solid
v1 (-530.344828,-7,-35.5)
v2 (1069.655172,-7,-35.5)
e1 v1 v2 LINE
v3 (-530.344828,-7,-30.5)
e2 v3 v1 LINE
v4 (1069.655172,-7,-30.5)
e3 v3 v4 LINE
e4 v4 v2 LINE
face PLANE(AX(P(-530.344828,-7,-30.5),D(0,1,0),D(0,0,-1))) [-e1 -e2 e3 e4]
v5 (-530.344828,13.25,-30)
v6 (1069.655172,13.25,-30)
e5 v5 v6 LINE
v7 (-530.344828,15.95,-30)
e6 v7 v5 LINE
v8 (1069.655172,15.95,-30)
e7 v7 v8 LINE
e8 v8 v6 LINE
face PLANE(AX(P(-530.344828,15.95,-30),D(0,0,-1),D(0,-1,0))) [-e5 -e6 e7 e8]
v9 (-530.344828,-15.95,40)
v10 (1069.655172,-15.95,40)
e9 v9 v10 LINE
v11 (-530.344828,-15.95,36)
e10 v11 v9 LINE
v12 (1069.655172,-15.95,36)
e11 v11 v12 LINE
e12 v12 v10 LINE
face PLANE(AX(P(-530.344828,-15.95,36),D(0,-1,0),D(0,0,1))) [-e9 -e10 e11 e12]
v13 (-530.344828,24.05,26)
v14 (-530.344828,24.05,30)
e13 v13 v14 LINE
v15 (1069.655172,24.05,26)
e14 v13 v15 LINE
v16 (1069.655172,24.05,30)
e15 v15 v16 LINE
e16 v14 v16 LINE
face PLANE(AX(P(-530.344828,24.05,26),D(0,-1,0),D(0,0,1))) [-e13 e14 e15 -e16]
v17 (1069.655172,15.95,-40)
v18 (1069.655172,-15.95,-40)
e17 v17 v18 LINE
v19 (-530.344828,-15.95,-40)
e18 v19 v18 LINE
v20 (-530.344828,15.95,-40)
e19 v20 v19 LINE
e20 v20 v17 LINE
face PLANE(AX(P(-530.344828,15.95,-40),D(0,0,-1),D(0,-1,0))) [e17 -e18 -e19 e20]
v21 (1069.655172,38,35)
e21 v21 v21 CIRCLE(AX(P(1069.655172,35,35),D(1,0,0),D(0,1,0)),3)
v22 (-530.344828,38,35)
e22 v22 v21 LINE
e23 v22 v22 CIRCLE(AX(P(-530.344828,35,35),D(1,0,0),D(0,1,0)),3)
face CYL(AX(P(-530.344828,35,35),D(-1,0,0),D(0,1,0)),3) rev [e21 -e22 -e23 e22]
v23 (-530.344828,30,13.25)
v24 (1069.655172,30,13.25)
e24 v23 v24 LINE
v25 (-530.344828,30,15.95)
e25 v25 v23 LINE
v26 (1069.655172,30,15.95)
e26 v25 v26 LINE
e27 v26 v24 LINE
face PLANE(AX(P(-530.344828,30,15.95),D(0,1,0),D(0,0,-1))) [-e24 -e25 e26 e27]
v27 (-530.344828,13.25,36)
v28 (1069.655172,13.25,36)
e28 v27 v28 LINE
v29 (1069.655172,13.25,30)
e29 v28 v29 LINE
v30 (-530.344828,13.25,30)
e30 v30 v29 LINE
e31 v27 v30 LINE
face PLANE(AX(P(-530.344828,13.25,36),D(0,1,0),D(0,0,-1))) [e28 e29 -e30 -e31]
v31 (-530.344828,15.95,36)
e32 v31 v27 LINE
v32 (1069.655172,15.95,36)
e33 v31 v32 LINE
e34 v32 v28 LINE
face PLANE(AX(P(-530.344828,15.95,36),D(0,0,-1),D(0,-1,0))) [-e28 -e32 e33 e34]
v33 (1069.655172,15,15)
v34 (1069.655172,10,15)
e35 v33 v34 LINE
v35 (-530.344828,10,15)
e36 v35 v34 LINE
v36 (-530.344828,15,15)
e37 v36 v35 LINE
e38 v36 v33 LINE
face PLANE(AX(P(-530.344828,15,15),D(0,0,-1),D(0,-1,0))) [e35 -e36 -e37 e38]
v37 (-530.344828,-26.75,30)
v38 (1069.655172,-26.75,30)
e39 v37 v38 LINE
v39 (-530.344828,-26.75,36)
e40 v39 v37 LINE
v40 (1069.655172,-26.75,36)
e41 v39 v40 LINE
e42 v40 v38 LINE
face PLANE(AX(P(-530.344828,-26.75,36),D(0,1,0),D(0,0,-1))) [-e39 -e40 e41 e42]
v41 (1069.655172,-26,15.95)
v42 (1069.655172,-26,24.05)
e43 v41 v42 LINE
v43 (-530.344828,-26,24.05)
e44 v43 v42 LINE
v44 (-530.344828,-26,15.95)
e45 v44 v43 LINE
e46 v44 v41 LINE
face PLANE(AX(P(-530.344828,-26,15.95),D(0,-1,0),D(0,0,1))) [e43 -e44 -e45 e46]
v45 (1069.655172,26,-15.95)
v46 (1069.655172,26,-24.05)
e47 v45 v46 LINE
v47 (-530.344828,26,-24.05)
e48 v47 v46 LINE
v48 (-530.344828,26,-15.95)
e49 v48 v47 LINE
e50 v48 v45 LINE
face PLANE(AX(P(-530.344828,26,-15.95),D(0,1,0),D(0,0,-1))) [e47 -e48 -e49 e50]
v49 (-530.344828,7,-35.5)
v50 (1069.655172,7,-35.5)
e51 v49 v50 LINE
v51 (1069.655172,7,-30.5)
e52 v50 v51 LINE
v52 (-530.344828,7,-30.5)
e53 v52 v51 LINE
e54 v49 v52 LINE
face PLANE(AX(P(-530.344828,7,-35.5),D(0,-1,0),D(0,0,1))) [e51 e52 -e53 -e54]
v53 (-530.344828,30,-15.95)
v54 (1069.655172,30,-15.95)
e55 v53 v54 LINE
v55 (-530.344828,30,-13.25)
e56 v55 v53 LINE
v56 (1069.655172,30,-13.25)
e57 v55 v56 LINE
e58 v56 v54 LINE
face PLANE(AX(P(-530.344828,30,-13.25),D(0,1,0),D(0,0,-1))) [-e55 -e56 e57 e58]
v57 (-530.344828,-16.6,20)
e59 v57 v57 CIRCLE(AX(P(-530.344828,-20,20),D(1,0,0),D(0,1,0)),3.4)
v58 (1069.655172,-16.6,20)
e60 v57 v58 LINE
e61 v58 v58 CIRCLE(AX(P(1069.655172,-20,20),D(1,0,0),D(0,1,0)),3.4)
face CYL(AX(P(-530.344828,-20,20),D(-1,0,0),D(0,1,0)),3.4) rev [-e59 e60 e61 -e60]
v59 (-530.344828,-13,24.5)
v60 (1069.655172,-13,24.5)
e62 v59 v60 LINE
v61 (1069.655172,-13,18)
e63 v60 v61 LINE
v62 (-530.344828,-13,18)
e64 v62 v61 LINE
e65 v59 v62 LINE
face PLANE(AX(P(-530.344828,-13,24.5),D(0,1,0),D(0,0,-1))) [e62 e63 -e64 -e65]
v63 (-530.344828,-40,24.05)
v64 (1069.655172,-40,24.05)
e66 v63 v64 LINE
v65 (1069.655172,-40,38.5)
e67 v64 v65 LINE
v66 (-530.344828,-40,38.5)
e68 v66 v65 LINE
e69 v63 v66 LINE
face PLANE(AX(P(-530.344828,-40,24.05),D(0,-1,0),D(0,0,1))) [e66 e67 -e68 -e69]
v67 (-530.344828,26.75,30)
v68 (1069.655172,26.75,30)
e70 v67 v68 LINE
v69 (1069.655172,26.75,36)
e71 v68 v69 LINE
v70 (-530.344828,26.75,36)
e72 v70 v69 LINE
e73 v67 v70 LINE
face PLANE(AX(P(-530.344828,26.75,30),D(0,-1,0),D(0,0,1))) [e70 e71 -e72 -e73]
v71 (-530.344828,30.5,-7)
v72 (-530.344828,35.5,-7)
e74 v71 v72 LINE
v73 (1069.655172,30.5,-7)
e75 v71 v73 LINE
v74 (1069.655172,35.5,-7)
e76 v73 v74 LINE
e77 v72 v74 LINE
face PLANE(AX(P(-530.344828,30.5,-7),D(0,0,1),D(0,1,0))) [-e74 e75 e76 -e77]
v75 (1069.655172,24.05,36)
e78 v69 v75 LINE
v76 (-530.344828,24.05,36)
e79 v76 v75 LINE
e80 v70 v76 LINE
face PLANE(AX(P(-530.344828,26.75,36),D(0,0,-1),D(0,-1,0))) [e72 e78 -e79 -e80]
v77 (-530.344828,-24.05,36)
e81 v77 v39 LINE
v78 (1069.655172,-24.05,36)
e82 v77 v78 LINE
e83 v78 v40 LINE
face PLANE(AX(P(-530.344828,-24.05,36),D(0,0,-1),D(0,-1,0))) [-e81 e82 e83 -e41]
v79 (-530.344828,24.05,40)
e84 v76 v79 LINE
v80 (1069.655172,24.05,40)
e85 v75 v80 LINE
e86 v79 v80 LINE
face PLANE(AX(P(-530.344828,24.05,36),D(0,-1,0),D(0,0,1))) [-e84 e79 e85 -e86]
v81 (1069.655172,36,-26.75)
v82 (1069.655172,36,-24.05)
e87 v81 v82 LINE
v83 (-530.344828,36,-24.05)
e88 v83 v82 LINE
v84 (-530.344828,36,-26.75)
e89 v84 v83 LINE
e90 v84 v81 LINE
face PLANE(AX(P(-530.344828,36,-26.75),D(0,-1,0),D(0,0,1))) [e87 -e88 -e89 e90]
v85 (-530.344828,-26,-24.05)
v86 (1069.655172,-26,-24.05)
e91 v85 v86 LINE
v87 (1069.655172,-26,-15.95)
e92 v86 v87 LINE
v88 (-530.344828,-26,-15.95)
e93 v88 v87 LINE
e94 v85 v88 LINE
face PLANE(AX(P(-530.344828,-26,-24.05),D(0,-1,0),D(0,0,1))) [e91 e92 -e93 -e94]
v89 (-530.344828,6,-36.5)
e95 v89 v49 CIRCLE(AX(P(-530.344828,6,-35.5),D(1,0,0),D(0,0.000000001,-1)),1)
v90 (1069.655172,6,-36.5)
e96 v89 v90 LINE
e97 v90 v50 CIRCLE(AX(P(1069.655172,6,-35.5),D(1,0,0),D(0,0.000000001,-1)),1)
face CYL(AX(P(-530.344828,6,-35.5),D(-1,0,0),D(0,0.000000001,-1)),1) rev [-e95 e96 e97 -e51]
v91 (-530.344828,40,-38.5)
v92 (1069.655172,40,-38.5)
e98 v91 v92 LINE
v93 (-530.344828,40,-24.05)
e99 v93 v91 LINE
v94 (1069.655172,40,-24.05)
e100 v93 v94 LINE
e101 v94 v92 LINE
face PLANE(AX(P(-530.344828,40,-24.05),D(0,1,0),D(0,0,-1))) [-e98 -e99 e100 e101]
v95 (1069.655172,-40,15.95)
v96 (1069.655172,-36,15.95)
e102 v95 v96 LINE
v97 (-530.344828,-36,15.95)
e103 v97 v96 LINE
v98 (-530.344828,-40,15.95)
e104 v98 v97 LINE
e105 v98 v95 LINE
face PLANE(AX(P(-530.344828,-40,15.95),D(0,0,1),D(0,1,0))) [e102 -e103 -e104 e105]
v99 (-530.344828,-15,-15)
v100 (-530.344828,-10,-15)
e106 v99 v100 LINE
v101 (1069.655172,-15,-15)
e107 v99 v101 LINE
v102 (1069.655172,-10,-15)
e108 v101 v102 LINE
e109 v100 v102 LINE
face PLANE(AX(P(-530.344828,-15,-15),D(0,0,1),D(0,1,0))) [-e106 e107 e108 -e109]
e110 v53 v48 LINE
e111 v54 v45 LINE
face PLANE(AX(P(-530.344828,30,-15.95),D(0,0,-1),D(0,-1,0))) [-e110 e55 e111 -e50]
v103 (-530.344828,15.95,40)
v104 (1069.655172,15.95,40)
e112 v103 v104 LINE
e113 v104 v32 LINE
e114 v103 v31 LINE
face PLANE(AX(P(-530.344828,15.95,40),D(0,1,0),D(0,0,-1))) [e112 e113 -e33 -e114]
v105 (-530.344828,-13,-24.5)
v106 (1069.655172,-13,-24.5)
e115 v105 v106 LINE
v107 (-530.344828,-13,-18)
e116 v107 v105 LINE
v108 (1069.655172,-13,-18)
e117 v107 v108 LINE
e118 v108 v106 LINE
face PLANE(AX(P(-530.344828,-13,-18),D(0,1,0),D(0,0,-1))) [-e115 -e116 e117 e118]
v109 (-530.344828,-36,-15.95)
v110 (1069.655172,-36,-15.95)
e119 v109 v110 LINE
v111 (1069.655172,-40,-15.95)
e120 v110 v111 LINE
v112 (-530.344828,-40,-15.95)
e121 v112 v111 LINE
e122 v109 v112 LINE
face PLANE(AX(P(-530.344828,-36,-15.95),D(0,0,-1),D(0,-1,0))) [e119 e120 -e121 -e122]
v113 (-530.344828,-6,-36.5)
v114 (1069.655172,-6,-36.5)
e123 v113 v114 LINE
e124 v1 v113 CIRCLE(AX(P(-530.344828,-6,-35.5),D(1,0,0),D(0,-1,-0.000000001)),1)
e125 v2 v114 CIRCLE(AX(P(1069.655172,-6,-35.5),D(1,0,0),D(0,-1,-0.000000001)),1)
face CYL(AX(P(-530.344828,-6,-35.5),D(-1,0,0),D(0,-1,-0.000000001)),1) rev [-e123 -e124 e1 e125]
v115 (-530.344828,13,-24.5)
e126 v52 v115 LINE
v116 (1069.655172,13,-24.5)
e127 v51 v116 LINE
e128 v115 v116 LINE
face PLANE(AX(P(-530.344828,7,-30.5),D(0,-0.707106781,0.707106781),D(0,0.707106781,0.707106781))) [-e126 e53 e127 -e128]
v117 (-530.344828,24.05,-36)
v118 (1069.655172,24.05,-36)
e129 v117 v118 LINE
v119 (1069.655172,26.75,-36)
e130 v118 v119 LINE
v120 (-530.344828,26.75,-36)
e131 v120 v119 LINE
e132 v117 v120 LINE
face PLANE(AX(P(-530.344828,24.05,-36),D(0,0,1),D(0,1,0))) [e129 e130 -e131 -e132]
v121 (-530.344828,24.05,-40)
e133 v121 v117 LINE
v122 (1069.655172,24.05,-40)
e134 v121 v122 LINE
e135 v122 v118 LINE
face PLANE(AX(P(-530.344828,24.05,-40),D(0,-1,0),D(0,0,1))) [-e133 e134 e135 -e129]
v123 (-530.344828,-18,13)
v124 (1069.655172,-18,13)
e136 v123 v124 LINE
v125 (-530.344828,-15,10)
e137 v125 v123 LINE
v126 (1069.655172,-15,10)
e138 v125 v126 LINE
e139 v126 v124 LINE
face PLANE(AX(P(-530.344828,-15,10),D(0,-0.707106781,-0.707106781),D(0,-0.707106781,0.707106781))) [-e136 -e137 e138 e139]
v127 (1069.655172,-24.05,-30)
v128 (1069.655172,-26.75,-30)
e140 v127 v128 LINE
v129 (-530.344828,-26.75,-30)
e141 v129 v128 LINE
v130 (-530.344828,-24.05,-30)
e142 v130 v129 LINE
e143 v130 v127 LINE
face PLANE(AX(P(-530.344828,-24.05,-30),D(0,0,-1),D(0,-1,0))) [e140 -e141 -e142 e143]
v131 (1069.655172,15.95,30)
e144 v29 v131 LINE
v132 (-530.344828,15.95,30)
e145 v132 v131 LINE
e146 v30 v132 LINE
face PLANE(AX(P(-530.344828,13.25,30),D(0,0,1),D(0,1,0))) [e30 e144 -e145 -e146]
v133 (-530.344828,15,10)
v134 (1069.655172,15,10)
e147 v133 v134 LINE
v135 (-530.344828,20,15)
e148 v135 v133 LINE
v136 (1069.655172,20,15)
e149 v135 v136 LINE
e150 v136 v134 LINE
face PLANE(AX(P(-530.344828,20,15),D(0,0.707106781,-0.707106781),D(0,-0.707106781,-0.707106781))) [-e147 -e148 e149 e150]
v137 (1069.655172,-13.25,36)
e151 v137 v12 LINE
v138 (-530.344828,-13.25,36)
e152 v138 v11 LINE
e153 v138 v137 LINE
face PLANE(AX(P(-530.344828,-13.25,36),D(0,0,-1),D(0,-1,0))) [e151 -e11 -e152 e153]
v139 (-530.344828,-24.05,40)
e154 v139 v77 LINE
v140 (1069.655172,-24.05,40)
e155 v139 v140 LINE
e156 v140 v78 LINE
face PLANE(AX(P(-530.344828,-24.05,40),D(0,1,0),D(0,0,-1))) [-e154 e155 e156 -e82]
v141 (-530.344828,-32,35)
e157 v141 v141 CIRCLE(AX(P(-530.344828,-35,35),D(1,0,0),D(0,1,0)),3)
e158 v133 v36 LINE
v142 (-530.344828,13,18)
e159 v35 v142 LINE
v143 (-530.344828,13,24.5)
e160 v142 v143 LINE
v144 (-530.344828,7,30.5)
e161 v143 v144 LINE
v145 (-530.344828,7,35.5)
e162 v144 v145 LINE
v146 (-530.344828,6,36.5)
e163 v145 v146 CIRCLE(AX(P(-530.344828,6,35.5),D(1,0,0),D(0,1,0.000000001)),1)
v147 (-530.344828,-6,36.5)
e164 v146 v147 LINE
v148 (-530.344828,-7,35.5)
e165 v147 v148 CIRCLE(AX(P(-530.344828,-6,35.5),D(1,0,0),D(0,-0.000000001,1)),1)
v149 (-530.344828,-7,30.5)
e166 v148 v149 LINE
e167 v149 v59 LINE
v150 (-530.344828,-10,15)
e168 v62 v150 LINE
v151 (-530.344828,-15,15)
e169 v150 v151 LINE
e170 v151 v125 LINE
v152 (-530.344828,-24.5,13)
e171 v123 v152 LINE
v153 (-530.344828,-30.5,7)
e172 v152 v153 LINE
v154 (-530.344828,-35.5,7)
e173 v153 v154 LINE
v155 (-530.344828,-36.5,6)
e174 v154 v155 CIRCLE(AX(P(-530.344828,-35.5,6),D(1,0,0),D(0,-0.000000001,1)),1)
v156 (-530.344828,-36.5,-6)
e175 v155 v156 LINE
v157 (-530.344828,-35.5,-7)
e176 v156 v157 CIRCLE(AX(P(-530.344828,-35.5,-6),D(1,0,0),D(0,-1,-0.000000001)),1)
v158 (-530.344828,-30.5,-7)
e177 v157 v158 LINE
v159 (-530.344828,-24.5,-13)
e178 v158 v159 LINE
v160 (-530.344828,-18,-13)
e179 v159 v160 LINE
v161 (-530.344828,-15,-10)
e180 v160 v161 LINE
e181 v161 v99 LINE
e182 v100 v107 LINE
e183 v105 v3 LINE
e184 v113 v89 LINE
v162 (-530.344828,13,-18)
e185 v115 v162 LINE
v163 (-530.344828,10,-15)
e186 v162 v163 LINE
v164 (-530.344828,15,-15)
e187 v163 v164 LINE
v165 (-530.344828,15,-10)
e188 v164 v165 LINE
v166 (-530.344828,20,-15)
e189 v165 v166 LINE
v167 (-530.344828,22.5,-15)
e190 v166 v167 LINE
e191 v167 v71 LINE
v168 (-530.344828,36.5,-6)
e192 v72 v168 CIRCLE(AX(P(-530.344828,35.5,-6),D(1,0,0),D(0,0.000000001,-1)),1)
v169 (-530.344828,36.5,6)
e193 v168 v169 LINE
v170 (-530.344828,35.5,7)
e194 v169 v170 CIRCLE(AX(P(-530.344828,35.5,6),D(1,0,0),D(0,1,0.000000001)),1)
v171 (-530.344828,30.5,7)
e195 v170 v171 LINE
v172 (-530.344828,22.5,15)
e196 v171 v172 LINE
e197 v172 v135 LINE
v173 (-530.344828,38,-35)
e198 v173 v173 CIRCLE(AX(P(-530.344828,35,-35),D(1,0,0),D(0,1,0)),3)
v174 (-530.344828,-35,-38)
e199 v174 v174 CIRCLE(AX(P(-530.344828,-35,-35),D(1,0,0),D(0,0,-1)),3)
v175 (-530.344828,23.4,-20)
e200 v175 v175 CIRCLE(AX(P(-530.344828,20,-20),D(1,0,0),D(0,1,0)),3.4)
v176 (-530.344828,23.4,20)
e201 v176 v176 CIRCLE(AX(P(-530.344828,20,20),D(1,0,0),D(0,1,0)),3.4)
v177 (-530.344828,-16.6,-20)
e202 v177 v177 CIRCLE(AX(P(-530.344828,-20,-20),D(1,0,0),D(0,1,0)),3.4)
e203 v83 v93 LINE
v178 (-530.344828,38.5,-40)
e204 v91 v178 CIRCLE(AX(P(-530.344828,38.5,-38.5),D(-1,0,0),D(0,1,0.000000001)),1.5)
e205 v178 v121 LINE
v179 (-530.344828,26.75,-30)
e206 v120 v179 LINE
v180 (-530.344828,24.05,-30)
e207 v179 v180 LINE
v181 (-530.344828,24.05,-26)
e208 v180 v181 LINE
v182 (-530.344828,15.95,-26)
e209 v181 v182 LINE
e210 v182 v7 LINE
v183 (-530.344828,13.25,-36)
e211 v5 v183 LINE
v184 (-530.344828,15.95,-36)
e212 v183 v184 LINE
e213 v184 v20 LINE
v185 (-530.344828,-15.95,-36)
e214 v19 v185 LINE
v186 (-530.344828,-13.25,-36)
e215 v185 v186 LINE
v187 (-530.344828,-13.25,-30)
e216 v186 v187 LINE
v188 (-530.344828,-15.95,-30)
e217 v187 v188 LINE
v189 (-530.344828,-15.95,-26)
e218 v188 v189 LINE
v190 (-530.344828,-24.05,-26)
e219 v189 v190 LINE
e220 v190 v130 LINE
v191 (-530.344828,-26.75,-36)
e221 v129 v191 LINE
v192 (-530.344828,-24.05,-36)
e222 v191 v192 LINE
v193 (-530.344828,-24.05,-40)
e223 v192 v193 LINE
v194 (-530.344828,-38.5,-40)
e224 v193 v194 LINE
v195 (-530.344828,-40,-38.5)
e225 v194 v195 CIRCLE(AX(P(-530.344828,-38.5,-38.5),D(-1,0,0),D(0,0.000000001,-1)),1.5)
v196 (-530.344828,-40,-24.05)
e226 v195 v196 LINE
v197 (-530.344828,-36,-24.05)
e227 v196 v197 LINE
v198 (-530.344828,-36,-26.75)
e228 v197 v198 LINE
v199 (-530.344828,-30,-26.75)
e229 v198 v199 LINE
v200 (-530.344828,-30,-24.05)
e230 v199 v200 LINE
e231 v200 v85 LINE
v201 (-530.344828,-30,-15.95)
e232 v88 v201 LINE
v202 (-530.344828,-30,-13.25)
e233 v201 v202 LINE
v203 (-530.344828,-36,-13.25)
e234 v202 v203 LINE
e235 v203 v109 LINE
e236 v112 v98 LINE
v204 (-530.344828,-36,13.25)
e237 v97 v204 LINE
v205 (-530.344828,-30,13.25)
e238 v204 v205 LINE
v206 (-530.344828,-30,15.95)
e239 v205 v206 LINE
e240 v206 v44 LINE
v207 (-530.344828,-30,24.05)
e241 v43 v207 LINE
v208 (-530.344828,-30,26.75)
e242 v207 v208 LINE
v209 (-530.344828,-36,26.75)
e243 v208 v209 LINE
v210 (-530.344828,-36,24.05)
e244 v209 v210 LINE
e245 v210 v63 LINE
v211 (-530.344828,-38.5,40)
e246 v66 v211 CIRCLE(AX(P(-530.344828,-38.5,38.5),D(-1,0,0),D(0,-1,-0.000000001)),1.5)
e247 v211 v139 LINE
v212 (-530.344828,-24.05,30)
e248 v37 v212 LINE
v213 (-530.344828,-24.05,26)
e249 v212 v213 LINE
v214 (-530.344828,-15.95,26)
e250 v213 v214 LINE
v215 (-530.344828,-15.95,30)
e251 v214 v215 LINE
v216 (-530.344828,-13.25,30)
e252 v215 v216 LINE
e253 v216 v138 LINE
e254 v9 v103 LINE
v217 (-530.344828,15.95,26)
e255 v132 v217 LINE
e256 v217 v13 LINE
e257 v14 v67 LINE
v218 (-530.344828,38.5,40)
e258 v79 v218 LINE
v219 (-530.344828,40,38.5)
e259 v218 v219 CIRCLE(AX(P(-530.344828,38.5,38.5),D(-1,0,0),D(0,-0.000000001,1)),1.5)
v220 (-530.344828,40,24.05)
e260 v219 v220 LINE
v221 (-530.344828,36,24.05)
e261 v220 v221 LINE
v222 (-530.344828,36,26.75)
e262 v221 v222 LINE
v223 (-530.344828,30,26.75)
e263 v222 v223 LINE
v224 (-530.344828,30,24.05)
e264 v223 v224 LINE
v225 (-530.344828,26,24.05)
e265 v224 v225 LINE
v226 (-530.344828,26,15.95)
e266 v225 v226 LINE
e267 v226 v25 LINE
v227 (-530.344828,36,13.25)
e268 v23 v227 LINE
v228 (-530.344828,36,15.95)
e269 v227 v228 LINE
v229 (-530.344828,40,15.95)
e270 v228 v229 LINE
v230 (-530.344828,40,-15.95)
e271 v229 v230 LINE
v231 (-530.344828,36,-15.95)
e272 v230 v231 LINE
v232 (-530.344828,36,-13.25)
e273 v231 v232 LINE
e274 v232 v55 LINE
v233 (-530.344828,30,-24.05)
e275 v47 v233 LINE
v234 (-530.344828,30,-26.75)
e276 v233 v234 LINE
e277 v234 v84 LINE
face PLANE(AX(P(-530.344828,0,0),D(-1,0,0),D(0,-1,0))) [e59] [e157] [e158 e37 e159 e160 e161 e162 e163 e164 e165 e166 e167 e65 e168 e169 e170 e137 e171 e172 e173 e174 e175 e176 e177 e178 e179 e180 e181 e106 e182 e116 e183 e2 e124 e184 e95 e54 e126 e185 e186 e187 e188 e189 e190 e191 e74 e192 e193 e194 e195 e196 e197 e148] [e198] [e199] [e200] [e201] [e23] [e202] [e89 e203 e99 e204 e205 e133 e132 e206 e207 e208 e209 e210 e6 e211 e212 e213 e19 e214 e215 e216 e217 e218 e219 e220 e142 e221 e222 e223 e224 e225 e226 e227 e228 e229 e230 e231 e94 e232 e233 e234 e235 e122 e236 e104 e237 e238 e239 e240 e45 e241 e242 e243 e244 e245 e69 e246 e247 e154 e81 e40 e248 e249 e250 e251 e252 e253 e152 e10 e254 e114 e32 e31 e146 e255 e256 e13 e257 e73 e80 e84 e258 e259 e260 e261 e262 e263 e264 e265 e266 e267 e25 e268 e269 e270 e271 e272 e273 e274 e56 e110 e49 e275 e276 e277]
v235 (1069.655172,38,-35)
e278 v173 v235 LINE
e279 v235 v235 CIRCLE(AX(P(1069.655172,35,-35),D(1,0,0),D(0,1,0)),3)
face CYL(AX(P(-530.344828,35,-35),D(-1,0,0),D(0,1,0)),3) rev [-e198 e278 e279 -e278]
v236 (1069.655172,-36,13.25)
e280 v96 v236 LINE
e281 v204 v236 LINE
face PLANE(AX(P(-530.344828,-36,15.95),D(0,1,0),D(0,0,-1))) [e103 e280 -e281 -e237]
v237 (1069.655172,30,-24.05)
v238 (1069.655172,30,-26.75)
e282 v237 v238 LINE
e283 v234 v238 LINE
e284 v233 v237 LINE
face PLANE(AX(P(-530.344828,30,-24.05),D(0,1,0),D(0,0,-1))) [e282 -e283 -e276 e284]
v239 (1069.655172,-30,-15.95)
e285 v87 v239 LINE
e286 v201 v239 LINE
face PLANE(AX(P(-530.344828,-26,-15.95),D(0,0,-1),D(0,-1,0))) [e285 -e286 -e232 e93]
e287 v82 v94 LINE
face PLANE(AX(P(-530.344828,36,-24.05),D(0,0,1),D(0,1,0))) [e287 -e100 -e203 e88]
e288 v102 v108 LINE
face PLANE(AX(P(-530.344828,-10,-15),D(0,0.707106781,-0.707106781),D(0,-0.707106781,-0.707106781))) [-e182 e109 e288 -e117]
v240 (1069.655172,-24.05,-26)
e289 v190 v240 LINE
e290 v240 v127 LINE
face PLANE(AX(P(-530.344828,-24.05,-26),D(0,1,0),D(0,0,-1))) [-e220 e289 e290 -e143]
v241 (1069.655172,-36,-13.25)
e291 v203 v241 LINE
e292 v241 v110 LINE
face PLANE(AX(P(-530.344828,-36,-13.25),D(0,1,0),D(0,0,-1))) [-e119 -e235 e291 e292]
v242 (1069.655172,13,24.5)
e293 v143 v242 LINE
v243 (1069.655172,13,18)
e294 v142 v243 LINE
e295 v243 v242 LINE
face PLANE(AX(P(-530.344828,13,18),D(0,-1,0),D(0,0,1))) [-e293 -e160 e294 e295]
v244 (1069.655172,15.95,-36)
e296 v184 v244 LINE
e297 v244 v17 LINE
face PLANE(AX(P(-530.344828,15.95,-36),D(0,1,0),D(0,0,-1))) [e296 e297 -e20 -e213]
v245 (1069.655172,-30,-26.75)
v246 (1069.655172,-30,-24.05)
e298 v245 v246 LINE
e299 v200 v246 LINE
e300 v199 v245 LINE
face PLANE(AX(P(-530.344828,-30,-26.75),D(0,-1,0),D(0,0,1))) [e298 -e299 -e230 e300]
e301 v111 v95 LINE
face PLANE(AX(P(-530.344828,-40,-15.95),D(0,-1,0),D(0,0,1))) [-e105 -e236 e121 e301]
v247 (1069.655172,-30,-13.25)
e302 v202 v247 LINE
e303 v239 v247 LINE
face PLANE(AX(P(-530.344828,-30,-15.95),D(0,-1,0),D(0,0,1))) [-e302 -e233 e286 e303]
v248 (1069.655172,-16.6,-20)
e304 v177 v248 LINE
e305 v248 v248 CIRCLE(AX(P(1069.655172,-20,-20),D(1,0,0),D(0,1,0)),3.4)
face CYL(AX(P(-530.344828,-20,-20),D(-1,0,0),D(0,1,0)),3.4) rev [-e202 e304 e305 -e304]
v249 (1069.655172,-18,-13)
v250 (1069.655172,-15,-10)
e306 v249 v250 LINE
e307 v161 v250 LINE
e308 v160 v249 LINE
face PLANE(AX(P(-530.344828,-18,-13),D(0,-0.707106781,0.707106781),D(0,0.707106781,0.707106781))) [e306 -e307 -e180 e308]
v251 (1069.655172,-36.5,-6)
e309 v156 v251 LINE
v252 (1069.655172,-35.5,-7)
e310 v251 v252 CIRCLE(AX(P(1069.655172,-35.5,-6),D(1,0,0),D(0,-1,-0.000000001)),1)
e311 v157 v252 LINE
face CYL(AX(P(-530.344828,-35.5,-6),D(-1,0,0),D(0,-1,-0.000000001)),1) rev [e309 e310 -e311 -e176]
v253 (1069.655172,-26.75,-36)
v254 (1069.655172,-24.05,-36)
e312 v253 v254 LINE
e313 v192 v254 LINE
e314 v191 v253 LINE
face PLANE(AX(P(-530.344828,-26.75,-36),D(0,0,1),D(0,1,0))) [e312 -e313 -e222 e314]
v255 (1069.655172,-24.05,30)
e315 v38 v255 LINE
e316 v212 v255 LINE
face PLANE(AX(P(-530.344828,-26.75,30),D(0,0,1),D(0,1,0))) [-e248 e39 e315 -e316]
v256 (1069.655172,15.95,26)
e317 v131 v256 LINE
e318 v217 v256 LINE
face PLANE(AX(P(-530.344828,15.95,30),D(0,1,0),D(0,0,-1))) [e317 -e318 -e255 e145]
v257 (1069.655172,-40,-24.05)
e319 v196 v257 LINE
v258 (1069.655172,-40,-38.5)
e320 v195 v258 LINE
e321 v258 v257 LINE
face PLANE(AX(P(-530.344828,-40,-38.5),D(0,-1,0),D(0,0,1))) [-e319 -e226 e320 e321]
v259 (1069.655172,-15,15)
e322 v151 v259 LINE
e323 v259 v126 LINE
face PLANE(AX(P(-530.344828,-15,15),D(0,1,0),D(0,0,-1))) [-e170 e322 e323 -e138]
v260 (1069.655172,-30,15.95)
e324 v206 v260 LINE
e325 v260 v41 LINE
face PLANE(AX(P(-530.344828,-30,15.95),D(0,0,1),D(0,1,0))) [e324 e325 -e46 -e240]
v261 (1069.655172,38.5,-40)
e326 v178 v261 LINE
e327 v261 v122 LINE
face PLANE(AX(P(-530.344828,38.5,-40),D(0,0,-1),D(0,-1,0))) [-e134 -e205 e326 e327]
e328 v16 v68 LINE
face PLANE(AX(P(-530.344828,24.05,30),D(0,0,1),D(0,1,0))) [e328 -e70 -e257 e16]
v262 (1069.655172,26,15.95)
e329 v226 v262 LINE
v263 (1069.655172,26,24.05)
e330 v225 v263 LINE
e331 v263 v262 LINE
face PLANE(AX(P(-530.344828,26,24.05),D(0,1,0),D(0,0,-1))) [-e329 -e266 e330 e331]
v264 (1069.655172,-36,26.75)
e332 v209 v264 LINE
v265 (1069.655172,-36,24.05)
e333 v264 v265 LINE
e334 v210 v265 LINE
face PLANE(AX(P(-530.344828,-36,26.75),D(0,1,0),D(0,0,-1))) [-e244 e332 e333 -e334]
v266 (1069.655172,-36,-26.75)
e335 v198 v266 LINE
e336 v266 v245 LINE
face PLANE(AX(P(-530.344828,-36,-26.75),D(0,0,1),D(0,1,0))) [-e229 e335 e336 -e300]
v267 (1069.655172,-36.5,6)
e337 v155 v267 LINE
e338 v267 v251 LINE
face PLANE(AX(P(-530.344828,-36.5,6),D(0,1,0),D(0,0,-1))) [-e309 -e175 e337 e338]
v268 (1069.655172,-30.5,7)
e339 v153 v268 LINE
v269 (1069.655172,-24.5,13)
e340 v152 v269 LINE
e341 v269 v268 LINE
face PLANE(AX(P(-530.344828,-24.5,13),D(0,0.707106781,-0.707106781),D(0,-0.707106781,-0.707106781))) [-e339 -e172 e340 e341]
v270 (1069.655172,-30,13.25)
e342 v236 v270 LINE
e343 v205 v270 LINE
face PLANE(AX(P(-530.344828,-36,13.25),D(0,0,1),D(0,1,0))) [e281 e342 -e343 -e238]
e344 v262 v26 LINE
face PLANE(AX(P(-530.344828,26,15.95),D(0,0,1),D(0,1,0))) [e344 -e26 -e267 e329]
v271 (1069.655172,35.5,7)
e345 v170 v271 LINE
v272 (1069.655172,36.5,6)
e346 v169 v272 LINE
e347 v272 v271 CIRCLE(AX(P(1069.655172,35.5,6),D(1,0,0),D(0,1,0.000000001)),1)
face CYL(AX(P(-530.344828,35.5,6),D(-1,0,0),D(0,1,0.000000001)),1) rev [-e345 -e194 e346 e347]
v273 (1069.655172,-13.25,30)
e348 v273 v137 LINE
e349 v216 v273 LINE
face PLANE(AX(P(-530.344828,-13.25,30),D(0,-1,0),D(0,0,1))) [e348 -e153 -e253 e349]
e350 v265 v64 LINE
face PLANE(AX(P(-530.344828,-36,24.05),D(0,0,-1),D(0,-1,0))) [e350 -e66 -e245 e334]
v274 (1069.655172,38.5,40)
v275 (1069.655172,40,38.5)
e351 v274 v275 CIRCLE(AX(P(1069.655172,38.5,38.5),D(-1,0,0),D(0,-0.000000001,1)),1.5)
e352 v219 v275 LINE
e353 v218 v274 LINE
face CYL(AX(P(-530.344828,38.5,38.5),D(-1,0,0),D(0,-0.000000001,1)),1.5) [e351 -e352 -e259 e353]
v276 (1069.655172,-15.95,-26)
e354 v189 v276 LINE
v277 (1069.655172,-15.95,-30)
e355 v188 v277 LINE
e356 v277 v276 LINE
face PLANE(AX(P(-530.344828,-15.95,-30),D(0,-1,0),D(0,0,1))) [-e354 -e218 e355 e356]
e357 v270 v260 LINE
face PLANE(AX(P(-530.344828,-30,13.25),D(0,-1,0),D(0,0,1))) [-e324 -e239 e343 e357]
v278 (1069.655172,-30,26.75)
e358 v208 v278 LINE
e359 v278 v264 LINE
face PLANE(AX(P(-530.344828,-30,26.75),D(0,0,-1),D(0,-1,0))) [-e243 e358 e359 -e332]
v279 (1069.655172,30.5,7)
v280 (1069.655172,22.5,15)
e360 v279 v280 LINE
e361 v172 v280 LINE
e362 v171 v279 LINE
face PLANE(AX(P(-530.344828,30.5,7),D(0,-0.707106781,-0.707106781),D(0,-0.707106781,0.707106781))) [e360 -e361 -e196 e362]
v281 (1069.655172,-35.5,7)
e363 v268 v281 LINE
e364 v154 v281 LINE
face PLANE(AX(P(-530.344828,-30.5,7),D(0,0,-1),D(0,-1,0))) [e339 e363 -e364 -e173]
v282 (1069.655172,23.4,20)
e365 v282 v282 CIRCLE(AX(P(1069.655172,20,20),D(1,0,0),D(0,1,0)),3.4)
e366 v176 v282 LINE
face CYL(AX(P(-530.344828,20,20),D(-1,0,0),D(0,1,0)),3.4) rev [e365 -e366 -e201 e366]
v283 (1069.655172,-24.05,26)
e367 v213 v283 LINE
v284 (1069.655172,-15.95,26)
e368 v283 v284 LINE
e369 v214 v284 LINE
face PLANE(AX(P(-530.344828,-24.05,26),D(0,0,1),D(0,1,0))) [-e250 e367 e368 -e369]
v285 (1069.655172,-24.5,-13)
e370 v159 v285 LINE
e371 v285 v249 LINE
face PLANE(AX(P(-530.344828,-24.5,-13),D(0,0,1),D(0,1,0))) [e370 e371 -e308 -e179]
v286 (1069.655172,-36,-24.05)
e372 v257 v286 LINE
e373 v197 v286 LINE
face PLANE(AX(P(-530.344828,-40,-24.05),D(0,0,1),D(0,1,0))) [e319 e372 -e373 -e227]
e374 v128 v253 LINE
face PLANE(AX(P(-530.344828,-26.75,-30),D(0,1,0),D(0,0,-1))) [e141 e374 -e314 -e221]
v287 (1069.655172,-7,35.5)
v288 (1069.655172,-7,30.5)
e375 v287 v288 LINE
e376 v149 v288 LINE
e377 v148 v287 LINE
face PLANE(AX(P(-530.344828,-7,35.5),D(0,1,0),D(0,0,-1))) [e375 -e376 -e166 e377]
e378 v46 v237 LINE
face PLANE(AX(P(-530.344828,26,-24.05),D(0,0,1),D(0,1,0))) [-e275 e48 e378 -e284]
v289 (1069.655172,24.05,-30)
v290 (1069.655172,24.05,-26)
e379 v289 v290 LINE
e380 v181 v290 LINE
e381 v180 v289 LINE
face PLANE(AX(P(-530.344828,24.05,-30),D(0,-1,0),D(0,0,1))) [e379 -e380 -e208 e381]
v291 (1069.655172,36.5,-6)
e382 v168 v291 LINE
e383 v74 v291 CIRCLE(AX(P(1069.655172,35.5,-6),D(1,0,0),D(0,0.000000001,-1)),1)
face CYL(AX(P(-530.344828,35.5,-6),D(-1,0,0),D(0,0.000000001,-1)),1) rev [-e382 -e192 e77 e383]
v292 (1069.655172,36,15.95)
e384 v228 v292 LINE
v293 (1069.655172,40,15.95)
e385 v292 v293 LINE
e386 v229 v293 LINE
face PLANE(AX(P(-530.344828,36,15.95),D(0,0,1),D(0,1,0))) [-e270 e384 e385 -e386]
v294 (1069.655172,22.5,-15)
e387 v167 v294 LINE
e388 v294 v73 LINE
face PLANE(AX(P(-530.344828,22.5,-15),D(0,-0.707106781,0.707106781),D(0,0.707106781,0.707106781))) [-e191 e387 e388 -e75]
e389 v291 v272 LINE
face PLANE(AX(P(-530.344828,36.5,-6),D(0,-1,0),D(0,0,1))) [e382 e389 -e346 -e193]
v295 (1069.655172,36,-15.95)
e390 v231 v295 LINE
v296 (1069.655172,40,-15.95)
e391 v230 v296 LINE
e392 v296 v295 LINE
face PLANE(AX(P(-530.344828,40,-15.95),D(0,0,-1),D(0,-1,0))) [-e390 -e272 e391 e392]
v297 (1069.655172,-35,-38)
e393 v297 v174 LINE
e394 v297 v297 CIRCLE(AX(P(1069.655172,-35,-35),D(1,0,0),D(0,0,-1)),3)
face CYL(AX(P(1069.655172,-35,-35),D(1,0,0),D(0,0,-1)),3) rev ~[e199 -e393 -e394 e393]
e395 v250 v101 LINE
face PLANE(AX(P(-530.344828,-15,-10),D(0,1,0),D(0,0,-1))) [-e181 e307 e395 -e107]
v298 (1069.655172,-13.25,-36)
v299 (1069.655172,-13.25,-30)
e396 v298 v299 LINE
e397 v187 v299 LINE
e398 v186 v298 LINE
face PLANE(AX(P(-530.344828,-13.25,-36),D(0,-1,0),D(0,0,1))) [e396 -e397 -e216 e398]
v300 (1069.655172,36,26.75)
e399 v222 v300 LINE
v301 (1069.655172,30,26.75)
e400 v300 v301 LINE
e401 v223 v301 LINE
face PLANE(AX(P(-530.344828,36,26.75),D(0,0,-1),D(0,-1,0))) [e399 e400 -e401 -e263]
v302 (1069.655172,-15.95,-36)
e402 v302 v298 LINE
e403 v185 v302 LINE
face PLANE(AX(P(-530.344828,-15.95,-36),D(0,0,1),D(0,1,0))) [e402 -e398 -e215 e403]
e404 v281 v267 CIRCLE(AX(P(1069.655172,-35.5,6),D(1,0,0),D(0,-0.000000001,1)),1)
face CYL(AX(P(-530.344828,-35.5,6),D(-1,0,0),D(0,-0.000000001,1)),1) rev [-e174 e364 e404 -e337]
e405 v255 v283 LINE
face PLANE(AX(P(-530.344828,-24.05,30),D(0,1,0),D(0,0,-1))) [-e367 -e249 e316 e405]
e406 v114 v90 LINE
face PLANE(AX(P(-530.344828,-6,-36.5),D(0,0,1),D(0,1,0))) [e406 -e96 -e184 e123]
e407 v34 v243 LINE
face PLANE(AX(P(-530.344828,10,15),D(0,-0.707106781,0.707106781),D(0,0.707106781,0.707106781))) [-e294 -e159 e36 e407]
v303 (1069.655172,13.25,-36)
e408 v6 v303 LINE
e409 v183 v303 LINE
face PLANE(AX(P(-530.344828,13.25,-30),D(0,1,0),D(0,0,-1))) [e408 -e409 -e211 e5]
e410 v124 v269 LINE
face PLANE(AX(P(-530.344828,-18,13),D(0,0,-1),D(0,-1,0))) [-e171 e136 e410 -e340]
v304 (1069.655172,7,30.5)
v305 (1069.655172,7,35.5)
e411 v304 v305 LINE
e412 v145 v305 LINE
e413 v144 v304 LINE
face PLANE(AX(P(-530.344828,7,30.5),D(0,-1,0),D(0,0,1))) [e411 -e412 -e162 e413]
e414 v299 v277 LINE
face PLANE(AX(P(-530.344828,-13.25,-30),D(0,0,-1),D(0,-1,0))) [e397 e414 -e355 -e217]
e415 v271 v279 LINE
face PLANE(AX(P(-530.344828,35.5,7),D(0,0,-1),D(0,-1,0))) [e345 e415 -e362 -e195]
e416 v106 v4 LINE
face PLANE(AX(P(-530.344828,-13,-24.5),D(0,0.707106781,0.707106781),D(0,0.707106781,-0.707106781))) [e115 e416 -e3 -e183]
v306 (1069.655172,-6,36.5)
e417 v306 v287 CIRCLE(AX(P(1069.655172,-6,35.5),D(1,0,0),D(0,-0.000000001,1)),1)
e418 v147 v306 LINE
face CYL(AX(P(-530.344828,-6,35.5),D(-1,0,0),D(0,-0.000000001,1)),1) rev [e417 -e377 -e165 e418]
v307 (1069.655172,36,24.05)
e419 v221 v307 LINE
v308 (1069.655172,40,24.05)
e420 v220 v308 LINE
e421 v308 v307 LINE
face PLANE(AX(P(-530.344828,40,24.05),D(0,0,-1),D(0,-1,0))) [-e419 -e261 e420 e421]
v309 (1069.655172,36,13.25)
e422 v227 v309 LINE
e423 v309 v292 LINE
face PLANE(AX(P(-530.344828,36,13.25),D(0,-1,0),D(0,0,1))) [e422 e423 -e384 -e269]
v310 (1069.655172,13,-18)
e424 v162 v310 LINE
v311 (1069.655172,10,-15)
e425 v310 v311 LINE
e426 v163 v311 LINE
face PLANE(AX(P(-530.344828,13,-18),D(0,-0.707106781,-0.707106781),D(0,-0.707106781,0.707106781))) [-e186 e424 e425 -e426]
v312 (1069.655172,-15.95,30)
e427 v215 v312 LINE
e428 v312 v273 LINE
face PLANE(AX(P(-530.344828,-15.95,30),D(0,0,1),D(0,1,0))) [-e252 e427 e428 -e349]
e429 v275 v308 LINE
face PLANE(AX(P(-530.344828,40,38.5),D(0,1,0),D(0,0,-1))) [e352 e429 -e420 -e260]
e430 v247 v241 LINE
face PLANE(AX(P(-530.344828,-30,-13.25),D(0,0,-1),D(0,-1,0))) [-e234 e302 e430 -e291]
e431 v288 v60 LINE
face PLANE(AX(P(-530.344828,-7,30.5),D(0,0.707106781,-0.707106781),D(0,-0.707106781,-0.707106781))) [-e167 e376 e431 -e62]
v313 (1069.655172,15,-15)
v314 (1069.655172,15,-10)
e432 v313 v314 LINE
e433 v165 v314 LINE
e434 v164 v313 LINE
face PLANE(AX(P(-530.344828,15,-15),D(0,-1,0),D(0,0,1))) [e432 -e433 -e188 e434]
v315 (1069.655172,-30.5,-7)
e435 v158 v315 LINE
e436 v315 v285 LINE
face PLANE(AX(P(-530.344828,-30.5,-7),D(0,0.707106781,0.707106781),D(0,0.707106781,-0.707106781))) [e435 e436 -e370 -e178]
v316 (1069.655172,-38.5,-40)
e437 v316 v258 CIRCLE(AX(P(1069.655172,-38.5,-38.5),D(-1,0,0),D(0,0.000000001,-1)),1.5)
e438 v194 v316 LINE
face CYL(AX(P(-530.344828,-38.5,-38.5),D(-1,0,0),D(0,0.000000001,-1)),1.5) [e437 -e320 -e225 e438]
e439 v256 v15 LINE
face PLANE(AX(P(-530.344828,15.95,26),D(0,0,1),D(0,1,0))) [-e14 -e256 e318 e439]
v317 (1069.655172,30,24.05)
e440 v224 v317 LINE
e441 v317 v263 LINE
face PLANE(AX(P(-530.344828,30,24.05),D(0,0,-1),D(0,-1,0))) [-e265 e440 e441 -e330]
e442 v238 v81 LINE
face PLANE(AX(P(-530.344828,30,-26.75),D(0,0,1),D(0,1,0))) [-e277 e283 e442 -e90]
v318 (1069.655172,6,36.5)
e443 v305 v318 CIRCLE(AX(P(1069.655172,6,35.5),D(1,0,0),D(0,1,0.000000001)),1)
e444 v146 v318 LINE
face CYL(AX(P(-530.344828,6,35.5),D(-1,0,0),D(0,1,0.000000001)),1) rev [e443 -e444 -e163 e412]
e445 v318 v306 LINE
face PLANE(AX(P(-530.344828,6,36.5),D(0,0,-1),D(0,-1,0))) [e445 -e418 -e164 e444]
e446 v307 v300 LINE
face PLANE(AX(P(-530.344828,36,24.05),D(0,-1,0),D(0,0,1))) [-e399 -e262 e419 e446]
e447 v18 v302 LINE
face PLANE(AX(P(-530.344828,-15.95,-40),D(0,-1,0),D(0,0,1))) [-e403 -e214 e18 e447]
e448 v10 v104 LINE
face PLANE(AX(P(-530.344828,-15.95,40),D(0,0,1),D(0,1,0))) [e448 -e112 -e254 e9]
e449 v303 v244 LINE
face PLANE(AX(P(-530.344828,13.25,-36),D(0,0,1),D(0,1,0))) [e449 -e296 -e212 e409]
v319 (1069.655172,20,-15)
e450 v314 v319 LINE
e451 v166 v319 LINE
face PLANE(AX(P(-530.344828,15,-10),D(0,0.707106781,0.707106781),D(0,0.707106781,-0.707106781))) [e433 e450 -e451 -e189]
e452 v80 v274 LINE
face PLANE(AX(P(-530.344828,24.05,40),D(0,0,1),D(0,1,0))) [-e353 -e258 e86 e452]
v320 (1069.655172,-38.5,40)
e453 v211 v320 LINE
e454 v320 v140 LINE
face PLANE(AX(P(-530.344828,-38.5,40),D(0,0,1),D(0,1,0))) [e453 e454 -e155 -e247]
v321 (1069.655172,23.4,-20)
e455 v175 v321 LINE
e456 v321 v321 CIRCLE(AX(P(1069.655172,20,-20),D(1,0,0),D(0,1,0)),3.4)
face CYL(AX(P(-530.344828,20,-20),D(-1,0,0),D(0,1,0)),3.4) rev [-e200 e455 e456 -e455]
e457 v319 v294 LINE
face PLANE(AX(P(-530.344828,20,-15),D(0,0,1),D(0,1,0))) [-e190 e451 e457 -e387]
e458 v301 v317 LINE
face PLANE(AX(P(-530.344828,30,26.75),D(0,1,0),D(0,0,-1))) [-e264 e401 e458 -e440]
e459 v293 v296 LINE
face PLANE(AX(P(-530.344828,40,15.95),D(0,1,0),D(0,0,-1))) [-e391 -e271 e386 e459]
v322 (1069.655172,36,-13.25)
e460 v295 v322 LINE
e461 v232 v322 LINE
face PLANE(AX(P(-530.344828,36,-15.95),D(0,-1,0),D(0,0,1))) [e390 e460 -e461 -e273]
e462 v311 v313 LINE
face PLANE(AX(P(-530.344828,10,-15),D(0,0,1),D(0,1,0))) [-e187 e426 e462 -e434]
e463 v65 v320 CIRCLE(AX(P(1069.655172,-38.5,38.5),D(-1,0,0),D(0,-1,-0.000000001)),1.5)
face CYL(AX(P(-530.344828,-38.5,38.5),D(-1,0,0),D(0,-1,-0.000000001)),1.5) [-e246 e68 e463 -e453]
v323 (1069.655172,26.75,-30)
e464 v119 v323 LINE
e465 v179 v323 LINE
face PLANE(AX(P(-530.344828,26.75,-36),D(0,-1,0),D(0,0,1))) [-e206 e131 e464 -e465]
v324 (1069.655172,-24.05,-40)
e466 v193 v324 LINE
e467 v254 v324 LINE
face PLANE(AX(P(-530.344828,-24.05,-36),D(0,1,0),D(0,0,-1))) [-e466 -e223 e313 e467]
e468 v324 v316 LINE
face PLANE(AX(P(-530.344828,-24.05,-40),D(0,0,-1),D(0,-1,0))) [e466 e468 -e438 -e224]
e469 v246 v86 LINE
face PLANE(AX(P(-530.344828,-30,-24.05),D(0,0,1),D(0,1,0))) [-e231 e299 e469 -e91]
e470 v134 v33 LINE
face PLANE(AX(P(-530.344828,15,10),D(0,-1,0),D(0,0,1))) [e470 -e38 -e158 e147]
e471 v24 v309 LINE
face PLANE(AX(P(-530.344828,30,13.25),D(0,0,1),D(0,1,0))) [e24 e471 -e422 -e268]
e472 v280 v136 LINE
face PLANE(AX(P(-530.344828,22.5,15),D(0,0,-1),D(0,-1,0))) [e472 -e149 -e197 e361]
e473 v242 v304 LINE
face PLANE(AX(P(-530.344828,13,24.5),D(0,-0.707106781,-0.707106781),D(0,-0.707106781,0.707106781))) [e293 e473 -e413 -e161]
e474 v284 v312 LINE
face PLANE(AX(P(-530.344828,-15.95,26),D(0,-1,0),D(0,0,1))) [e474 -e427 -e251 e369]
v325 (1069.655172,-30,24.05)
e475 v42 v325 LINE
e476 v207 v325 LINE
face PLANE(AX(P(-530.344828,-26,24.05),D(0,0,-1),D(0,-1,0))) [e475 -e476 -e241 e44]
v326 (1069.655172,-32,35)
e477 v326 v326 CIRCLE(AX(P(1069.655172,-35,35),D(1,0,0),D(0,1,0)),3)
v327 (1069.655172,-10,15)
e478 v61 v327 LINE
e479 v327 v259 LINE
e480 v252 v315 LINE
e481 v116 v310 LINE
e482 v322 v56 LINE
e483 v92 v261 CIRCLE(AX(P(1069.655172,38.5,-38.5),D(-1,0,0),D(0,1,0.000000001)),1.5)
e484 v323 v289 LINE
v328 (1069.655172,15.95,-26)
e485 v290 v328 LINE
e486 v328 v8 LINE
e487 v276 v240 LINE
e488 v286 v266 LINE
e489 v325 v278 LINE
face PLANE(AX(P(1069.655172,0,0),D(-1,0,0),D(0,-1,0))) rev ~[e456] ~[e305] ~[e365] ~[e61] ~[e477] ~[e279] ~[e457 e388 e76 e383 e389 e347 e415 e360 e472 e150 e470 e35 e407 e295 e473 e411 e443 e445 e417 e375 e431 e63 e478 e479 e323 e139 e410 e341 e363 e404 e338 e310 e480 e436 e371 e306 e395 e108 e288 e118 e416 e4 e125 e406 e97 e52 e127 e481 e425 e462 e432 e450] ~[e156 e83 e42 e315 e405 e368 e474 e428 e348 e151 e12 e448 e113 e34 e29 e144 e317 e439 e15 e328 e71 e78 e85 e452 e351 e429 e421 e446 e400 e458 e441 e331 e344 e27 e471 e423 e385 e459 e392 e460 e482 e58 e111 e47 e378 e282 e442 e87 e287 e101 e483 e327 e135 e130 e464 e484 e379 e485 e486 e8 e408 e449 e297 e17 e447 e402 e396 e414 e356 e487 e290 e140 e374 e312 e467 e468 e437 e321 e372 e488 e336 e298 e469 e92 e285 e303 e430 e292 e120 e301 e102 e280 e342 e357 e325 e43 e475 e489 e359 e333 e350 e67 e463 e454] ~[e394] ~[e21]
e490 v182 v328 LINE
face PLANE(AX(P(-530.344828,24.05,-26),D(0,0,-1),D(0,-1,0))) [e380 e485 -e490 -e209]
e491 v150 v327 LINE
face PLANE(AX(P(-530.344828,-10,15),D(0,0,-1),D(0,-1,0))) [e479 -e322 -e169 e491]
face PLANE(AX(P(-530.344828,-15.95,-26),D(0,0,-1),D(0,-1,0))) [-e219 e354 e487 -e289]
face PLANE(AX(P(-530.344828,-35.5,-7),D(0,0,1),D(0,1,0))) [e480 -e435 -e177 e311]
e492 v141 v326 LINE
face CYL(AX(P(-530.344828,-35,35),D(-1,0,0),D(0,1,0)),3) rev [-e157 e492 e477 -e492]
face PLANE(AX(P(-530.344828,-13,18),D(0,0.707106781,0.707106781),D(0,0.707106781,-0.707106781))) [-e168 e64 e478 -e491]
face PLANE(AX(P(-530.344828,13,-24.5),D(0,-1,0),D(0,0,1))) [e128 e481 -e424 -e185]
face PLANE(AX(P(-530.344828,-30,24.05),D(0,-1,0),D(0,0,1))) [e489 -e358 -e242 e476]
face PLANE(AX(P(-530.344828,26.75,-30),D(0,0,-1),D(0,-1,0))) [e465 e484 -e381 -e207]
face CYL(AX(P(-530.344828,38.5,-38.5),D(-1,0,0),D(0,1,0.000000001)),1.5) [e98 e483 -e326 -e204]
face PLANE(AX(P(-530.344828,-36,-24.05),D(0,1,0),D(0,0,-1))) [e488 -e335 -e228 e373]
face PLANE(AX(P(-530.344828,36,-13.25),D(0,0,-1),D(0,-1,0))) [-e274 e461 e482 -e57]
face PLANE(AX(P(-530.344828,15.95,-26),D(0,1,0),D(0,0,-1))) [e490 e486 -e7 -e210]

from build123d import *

# Parameters (mm, degrees)
SKETCH1_R                                 = 3.4
SKETCH1_R_2                               = 3
ALUMINIUM_PROFILE_80_X_80G_X_R1_5_1_DEPTH = 1600
SKETCH10_R                                = 3
CUT_EXTRUDE1_DEPTH                        = 1601.999687695


with BuildPart() as part:
    # Sketch1 → Aluminium profile 80 X 80G X R1.5(1) (new body)
    with BuildSketch(Plane.YZ.offset(-530.344827586)):
        with BuildLine():
            Line((-24.05, 40), (-24.05, 36))
            Line((-24.05, 36), (-26.75, 36))
            Line((-26.75, 36), (-26.75, 30))
            Line((-26.75, 30), (-24.05, 30))
            Line((-24.05, 30), (-24.05, 26))
            Line((-24.05, 26), (-15.95, 26))
            Line((-15.95, 26), (-15.95, 30))
            Line((-15.95, 30), (-13.25, 30))
            Line((-13.25, 30), (-13.25, 36))
            Line((-13.25, 36), (-15.95, 36))
            Line((-15.95, 36), (-15.95, 40))
            Line((-15.95, 40), (15.95, 40))
            Line((15.95, 40), (15.95, 36))
            Line((15.95, 36), (13.25, 36))
            Line((13.25, 36), (13.25, 30))
            Line((13.25, 30), (15.95, 30))
            Line((15.95, 30), (15.95, 26))
            Line((15.95, 26), (24.05, 26))
            Line((24.05, 26), (24.05, 30))
            Line((24.05, 30), (26.75, 30))
            Line((26.75, 30), (26.75, 36))
            Line((26.75, 36), (24.05, 36))
            Line((24.05, 36), (24.05, 40))
            Line((24.05, 40), (38.5, 40))
            ThreePointArc((38.5, 40), (39.560660172, 39.560660172), (40, 38.5))
            Line((40, 38.5), (40, 24.05))
            Line((40, 24.05), (36, 24.05))
            Line((36, 24.05), (36, 26.75))
            Line((36, 26.75), (30, 26.75))
            Line((30, 26.75), (30, 24.05))
            Line((30, 24.05), (26, 24.05))
            Line((26, 24.05), (26, 15.95))
            Line((26, 15.95), (30, 15.95))
            Line((30, 15.95), (30, 13.25))
            Line((30, 13.25), (36, 13.25))
            Line((36, 13.25), (36, 15.95))
            Line((36, 15.95), (40, 15.95))
            Line((40, 15.95), (40, -15.95))
            Line((40, -15.95), (36, -15.95))
            Line((36, -15.95), (36, -13.25))
            Line((36, -13.25), (30, -13.25))
            Line((30, -13.25), (30, -15.95))
            Line((30, -15.95), (26, -15.95))
            Line((26, -15.95), (26, -24.05))
            Line((26, -24.05), (30, -24.05))
            Line((30, -24.05), (30, -26.75))
            Line((30, -26.75), (36, -26.75))
            Line((36, -26.75), (36, -24.05))
            Line((36, -24.05), (40, -24.05))
            Line((40, -24.05), (40, -38.5))
            ThreePointArc((40, -38.5), (39.560660172, -39.560660172), (38.5, -40))
            Line((38.5, -40), (24.05, -40))
            Line((24.05, -40), (24.05, -36))
            Line((24.05, -36), (26.75, -36))
            Line((26.75, -36), (26.75, -30))
            Line((26.75, -30), (24.05, -30))
            Line((24.05, -30), (24.05, -26))
            Line((24.05, -26), (15.95, -26))
            Line((15.95, -26), (15.95, -30))
            Line((15.95, -30), (13.25, -30))
            Line((13.25, -30), (13.25, -36))
            Line((13.25, -36), (15.95, -36))
            Line((15.95, -36), (15.95, -40))
            Line((15.95, -40), (-15.95, -40))
            Line((-15.95, -40), (-15.95, -36))
            Line((-15.95, -36), (-13.25, -36))
            Line((-13.25, -36), (-13.25, -30))
            Line((-13.25, -30), (-15.95, -30))
            Line((-15.95, -30), (-15.95, -26))
            Line((-15.95, -26), (-24.05, -26))
            Line((-24.05, -26), (-24.05, -30))
            Line((-24.05, -30), (-26.75, -30))
            Line((-26.75, -30), (-26.75, -36))
            Line((-26.75, -36), (-24.05, -36))
            Line((-24.05, -36), (-24.05, -40))
            Line((-24.05, -40), (-38.5, -40))
            ThreePointArc((-38.5, -40), (-39.560660172, -39.560660172), (-40, -38.5))
            Line((-40, -38.5), (-40, -24.05))
            Line((-40, -24.05), (-36, -24.05))
            Line((-36, -24.05), (-36, -26.75))
            Line((-36, -26.75), (-30, -26.75))
            Line((-30, -26.75), (-30, -24.05))
            Line((-30, -24.05), (-26, -24.05))
            Line((-26, -24.05), (-26, -15.95))
            Line((-26, -15.95), (-30, -15.95))
            Line((-30, -15.95), (-30, -13.25))
            Line((-30, -13.25), (-36, -13.25))
            Line((-36, -13.25), (-36, -15.95))
            Line((-36, -15.95), (-40, -15.95))
            Line((-40, -15.95), (-40, 15.95))
            Line((-40, 15.95), (-36, 15.95))
            Line((-36, 15.95), (-36, 13.25))
            Line((-36, 13.25), (-30, 13.25))
            Line((-30, 13.25), (-30, 15.95))
            Line((-30, 15.95), (-26, 15.95))
            Line((-26, 15.95), (-26, 24.05))
            Line((-26, 24.05), (-30, 24.05))
            Line((-30, 24.05), (-30, 26.75))
            Line((-30, 26.75), (-36, 26.75))
            Line((-36, 26.75), (-36, 24.05))
            Line((-36, 24.05), (-40, 24.05))
            Line((-40, 24.05), (-40, 38.5))
            ThreePointArc((-40, 38.5), (-39.560660172, 39.560660172), (-38.5, 40))
            Line((-38.5, 40), (-24.05, 40))
        make_face()
        with Locations((-20, 20)):
            Circle(SKETCH1_R, mode=Mode.SUBTRACT)
        with Locations((20, 20)):
            Circle(SKETCH1_R, mode=Mode.SUBTRACT)
        with Locations((20, -20)):
            Circle(SKETCH1_R, mode=Mode.SUBTRACT)
        with Locations((-20, -20)):
            Circle(SKETCH1_R, mode=Mode.SUBTRACT)
        with Locations((-35, 35)):
            Circle(SKETCH1_R_2, mode=Mode.SUBTRACT)
        with Locations((35, 35)):
            Circle(SKETCH1_R_2, mode=Mode.SUBTRACT)
        with Locations((35, -35)):
            Circle(SKETCH1_R_2, mode=Mode.SUBTRACT)
        with BuildLine():
            Line((-13, 18), (-10, 15))
            Line((-10, 15), (-15, 15))
            Line((-15, 15), (-15, 10))
            Line((-15, 10), (-18, 13))
            Line((-18, 13), (-24.5, 13))
            Line((-24.5, 13), (-30.5, 7))
            Line((-30.5, 7), (-35.5, 7))
            ThreePointArc((-35.5, 7), (-36.207106781, 6.707106781), (-36.5, 6))
            Line((-36.5, 6), (-36.5, -6))
            ThreePointArc((-36.5, -6), (-36.207106781, -6.707106781), (-35.5, -7))
            Line((-35.5, -7), (-30.5, -7))
            Line((-30.5, -7), (-24.5, -13))
            Line((-24.5, -13), (-18, -13))
            Line((-18, -13), (-15, -10))
            Line((-15, -10), (-15, -15))
            Line((-15, -15), (-10, -15))
            Line((-10, -15), (-13, -18))
            Line((-13, -18), (-13, -24.5))
            Line((-13, -24.5), (-7, -30.5))
            Line((-7, -30.5), (-7, -35.5))
            ThreePointArc((-7, -35.5), (-6.707106781, -36.207106781), (-6, -36.5))
            Line((-6, -36.5), (6, -36.5))
            ThreePointArc((6, -36.5), (6.707106781, -36.207106781), (7, -35.5))
            Line((7, -35.5), (7, -30.5))
            Line((7, -30.5), (13, -24.5))
            Line((13, -24.5), (13, -18))
            Line((13, -18), (10, -15))
            Line((10, -15), (15, -15))
            Line((15, -15), (15, -10))
            Line((15, -10), (20, -15))
            Line((20, -15), (22.5, -15))
            Line((22.5, -15), (30.5, -7))
            Line((30.5, -7), (35.5, -7))
            ThreePointArc((35.5, -7), (36.207106781, -6.707106781), (36.5, -6))
            Line((36.5, -6), (36.5, 6))
            ThreePointArc((36.5, 6), (36.207106781, 6.707106781), (35.5, 7))
            Line((35.5, 7), (30.5, 7))
            Line((30.5, 7), (22.5, 15))
            Line((22.5, 15), (20, 15))
            Line((20, 15), (15, 10))
            Line((15, 10), (15, 15))
            Line((15, 15), (10, 15))
            Line((10, 15), (13, 18))
            Line((13, 18), (13, 24.5))
            Line((13, 24.5), (7, 30.5))
            Line((7, 30.5), (7, 35.5))
            ThreePointArc((7, 35.5), (6.707106781, 36.207106781), (6, 36.5))
            Line((6, 36.5), (-6, 36.5))
            ThreePointArc((-6, 36.5), (-6.707106781, 36.207106781), (-7, 35.5))
            Line((-7, 35.5), (-7, 30.5))
            Line((-7, 30.5), (-13, 24.5))
            Line((-13, 24.5), (-13, 18))
        make_face(mode=Mode.SUBTRACT)
    extrude(amount=ALUMINIUM_PROFILE_80_X_80G_X_R1_5_1_DEPTH)

    # Sketch10 → Cut-Extrude1 (cut, through all)
    with BuildSketch(Plane(origin=(1069.655172414, 0, 0), x_dir=(0, 0, -1), z_dir=(1, 0, 0))):
        with Locations((35, -35)):
            Circle(SKETCH10_R)
    extrude(amount=-CUT_EXTRUDE1_DEPTH, mode=Mode.SUBTRACT)


solid = part.part
